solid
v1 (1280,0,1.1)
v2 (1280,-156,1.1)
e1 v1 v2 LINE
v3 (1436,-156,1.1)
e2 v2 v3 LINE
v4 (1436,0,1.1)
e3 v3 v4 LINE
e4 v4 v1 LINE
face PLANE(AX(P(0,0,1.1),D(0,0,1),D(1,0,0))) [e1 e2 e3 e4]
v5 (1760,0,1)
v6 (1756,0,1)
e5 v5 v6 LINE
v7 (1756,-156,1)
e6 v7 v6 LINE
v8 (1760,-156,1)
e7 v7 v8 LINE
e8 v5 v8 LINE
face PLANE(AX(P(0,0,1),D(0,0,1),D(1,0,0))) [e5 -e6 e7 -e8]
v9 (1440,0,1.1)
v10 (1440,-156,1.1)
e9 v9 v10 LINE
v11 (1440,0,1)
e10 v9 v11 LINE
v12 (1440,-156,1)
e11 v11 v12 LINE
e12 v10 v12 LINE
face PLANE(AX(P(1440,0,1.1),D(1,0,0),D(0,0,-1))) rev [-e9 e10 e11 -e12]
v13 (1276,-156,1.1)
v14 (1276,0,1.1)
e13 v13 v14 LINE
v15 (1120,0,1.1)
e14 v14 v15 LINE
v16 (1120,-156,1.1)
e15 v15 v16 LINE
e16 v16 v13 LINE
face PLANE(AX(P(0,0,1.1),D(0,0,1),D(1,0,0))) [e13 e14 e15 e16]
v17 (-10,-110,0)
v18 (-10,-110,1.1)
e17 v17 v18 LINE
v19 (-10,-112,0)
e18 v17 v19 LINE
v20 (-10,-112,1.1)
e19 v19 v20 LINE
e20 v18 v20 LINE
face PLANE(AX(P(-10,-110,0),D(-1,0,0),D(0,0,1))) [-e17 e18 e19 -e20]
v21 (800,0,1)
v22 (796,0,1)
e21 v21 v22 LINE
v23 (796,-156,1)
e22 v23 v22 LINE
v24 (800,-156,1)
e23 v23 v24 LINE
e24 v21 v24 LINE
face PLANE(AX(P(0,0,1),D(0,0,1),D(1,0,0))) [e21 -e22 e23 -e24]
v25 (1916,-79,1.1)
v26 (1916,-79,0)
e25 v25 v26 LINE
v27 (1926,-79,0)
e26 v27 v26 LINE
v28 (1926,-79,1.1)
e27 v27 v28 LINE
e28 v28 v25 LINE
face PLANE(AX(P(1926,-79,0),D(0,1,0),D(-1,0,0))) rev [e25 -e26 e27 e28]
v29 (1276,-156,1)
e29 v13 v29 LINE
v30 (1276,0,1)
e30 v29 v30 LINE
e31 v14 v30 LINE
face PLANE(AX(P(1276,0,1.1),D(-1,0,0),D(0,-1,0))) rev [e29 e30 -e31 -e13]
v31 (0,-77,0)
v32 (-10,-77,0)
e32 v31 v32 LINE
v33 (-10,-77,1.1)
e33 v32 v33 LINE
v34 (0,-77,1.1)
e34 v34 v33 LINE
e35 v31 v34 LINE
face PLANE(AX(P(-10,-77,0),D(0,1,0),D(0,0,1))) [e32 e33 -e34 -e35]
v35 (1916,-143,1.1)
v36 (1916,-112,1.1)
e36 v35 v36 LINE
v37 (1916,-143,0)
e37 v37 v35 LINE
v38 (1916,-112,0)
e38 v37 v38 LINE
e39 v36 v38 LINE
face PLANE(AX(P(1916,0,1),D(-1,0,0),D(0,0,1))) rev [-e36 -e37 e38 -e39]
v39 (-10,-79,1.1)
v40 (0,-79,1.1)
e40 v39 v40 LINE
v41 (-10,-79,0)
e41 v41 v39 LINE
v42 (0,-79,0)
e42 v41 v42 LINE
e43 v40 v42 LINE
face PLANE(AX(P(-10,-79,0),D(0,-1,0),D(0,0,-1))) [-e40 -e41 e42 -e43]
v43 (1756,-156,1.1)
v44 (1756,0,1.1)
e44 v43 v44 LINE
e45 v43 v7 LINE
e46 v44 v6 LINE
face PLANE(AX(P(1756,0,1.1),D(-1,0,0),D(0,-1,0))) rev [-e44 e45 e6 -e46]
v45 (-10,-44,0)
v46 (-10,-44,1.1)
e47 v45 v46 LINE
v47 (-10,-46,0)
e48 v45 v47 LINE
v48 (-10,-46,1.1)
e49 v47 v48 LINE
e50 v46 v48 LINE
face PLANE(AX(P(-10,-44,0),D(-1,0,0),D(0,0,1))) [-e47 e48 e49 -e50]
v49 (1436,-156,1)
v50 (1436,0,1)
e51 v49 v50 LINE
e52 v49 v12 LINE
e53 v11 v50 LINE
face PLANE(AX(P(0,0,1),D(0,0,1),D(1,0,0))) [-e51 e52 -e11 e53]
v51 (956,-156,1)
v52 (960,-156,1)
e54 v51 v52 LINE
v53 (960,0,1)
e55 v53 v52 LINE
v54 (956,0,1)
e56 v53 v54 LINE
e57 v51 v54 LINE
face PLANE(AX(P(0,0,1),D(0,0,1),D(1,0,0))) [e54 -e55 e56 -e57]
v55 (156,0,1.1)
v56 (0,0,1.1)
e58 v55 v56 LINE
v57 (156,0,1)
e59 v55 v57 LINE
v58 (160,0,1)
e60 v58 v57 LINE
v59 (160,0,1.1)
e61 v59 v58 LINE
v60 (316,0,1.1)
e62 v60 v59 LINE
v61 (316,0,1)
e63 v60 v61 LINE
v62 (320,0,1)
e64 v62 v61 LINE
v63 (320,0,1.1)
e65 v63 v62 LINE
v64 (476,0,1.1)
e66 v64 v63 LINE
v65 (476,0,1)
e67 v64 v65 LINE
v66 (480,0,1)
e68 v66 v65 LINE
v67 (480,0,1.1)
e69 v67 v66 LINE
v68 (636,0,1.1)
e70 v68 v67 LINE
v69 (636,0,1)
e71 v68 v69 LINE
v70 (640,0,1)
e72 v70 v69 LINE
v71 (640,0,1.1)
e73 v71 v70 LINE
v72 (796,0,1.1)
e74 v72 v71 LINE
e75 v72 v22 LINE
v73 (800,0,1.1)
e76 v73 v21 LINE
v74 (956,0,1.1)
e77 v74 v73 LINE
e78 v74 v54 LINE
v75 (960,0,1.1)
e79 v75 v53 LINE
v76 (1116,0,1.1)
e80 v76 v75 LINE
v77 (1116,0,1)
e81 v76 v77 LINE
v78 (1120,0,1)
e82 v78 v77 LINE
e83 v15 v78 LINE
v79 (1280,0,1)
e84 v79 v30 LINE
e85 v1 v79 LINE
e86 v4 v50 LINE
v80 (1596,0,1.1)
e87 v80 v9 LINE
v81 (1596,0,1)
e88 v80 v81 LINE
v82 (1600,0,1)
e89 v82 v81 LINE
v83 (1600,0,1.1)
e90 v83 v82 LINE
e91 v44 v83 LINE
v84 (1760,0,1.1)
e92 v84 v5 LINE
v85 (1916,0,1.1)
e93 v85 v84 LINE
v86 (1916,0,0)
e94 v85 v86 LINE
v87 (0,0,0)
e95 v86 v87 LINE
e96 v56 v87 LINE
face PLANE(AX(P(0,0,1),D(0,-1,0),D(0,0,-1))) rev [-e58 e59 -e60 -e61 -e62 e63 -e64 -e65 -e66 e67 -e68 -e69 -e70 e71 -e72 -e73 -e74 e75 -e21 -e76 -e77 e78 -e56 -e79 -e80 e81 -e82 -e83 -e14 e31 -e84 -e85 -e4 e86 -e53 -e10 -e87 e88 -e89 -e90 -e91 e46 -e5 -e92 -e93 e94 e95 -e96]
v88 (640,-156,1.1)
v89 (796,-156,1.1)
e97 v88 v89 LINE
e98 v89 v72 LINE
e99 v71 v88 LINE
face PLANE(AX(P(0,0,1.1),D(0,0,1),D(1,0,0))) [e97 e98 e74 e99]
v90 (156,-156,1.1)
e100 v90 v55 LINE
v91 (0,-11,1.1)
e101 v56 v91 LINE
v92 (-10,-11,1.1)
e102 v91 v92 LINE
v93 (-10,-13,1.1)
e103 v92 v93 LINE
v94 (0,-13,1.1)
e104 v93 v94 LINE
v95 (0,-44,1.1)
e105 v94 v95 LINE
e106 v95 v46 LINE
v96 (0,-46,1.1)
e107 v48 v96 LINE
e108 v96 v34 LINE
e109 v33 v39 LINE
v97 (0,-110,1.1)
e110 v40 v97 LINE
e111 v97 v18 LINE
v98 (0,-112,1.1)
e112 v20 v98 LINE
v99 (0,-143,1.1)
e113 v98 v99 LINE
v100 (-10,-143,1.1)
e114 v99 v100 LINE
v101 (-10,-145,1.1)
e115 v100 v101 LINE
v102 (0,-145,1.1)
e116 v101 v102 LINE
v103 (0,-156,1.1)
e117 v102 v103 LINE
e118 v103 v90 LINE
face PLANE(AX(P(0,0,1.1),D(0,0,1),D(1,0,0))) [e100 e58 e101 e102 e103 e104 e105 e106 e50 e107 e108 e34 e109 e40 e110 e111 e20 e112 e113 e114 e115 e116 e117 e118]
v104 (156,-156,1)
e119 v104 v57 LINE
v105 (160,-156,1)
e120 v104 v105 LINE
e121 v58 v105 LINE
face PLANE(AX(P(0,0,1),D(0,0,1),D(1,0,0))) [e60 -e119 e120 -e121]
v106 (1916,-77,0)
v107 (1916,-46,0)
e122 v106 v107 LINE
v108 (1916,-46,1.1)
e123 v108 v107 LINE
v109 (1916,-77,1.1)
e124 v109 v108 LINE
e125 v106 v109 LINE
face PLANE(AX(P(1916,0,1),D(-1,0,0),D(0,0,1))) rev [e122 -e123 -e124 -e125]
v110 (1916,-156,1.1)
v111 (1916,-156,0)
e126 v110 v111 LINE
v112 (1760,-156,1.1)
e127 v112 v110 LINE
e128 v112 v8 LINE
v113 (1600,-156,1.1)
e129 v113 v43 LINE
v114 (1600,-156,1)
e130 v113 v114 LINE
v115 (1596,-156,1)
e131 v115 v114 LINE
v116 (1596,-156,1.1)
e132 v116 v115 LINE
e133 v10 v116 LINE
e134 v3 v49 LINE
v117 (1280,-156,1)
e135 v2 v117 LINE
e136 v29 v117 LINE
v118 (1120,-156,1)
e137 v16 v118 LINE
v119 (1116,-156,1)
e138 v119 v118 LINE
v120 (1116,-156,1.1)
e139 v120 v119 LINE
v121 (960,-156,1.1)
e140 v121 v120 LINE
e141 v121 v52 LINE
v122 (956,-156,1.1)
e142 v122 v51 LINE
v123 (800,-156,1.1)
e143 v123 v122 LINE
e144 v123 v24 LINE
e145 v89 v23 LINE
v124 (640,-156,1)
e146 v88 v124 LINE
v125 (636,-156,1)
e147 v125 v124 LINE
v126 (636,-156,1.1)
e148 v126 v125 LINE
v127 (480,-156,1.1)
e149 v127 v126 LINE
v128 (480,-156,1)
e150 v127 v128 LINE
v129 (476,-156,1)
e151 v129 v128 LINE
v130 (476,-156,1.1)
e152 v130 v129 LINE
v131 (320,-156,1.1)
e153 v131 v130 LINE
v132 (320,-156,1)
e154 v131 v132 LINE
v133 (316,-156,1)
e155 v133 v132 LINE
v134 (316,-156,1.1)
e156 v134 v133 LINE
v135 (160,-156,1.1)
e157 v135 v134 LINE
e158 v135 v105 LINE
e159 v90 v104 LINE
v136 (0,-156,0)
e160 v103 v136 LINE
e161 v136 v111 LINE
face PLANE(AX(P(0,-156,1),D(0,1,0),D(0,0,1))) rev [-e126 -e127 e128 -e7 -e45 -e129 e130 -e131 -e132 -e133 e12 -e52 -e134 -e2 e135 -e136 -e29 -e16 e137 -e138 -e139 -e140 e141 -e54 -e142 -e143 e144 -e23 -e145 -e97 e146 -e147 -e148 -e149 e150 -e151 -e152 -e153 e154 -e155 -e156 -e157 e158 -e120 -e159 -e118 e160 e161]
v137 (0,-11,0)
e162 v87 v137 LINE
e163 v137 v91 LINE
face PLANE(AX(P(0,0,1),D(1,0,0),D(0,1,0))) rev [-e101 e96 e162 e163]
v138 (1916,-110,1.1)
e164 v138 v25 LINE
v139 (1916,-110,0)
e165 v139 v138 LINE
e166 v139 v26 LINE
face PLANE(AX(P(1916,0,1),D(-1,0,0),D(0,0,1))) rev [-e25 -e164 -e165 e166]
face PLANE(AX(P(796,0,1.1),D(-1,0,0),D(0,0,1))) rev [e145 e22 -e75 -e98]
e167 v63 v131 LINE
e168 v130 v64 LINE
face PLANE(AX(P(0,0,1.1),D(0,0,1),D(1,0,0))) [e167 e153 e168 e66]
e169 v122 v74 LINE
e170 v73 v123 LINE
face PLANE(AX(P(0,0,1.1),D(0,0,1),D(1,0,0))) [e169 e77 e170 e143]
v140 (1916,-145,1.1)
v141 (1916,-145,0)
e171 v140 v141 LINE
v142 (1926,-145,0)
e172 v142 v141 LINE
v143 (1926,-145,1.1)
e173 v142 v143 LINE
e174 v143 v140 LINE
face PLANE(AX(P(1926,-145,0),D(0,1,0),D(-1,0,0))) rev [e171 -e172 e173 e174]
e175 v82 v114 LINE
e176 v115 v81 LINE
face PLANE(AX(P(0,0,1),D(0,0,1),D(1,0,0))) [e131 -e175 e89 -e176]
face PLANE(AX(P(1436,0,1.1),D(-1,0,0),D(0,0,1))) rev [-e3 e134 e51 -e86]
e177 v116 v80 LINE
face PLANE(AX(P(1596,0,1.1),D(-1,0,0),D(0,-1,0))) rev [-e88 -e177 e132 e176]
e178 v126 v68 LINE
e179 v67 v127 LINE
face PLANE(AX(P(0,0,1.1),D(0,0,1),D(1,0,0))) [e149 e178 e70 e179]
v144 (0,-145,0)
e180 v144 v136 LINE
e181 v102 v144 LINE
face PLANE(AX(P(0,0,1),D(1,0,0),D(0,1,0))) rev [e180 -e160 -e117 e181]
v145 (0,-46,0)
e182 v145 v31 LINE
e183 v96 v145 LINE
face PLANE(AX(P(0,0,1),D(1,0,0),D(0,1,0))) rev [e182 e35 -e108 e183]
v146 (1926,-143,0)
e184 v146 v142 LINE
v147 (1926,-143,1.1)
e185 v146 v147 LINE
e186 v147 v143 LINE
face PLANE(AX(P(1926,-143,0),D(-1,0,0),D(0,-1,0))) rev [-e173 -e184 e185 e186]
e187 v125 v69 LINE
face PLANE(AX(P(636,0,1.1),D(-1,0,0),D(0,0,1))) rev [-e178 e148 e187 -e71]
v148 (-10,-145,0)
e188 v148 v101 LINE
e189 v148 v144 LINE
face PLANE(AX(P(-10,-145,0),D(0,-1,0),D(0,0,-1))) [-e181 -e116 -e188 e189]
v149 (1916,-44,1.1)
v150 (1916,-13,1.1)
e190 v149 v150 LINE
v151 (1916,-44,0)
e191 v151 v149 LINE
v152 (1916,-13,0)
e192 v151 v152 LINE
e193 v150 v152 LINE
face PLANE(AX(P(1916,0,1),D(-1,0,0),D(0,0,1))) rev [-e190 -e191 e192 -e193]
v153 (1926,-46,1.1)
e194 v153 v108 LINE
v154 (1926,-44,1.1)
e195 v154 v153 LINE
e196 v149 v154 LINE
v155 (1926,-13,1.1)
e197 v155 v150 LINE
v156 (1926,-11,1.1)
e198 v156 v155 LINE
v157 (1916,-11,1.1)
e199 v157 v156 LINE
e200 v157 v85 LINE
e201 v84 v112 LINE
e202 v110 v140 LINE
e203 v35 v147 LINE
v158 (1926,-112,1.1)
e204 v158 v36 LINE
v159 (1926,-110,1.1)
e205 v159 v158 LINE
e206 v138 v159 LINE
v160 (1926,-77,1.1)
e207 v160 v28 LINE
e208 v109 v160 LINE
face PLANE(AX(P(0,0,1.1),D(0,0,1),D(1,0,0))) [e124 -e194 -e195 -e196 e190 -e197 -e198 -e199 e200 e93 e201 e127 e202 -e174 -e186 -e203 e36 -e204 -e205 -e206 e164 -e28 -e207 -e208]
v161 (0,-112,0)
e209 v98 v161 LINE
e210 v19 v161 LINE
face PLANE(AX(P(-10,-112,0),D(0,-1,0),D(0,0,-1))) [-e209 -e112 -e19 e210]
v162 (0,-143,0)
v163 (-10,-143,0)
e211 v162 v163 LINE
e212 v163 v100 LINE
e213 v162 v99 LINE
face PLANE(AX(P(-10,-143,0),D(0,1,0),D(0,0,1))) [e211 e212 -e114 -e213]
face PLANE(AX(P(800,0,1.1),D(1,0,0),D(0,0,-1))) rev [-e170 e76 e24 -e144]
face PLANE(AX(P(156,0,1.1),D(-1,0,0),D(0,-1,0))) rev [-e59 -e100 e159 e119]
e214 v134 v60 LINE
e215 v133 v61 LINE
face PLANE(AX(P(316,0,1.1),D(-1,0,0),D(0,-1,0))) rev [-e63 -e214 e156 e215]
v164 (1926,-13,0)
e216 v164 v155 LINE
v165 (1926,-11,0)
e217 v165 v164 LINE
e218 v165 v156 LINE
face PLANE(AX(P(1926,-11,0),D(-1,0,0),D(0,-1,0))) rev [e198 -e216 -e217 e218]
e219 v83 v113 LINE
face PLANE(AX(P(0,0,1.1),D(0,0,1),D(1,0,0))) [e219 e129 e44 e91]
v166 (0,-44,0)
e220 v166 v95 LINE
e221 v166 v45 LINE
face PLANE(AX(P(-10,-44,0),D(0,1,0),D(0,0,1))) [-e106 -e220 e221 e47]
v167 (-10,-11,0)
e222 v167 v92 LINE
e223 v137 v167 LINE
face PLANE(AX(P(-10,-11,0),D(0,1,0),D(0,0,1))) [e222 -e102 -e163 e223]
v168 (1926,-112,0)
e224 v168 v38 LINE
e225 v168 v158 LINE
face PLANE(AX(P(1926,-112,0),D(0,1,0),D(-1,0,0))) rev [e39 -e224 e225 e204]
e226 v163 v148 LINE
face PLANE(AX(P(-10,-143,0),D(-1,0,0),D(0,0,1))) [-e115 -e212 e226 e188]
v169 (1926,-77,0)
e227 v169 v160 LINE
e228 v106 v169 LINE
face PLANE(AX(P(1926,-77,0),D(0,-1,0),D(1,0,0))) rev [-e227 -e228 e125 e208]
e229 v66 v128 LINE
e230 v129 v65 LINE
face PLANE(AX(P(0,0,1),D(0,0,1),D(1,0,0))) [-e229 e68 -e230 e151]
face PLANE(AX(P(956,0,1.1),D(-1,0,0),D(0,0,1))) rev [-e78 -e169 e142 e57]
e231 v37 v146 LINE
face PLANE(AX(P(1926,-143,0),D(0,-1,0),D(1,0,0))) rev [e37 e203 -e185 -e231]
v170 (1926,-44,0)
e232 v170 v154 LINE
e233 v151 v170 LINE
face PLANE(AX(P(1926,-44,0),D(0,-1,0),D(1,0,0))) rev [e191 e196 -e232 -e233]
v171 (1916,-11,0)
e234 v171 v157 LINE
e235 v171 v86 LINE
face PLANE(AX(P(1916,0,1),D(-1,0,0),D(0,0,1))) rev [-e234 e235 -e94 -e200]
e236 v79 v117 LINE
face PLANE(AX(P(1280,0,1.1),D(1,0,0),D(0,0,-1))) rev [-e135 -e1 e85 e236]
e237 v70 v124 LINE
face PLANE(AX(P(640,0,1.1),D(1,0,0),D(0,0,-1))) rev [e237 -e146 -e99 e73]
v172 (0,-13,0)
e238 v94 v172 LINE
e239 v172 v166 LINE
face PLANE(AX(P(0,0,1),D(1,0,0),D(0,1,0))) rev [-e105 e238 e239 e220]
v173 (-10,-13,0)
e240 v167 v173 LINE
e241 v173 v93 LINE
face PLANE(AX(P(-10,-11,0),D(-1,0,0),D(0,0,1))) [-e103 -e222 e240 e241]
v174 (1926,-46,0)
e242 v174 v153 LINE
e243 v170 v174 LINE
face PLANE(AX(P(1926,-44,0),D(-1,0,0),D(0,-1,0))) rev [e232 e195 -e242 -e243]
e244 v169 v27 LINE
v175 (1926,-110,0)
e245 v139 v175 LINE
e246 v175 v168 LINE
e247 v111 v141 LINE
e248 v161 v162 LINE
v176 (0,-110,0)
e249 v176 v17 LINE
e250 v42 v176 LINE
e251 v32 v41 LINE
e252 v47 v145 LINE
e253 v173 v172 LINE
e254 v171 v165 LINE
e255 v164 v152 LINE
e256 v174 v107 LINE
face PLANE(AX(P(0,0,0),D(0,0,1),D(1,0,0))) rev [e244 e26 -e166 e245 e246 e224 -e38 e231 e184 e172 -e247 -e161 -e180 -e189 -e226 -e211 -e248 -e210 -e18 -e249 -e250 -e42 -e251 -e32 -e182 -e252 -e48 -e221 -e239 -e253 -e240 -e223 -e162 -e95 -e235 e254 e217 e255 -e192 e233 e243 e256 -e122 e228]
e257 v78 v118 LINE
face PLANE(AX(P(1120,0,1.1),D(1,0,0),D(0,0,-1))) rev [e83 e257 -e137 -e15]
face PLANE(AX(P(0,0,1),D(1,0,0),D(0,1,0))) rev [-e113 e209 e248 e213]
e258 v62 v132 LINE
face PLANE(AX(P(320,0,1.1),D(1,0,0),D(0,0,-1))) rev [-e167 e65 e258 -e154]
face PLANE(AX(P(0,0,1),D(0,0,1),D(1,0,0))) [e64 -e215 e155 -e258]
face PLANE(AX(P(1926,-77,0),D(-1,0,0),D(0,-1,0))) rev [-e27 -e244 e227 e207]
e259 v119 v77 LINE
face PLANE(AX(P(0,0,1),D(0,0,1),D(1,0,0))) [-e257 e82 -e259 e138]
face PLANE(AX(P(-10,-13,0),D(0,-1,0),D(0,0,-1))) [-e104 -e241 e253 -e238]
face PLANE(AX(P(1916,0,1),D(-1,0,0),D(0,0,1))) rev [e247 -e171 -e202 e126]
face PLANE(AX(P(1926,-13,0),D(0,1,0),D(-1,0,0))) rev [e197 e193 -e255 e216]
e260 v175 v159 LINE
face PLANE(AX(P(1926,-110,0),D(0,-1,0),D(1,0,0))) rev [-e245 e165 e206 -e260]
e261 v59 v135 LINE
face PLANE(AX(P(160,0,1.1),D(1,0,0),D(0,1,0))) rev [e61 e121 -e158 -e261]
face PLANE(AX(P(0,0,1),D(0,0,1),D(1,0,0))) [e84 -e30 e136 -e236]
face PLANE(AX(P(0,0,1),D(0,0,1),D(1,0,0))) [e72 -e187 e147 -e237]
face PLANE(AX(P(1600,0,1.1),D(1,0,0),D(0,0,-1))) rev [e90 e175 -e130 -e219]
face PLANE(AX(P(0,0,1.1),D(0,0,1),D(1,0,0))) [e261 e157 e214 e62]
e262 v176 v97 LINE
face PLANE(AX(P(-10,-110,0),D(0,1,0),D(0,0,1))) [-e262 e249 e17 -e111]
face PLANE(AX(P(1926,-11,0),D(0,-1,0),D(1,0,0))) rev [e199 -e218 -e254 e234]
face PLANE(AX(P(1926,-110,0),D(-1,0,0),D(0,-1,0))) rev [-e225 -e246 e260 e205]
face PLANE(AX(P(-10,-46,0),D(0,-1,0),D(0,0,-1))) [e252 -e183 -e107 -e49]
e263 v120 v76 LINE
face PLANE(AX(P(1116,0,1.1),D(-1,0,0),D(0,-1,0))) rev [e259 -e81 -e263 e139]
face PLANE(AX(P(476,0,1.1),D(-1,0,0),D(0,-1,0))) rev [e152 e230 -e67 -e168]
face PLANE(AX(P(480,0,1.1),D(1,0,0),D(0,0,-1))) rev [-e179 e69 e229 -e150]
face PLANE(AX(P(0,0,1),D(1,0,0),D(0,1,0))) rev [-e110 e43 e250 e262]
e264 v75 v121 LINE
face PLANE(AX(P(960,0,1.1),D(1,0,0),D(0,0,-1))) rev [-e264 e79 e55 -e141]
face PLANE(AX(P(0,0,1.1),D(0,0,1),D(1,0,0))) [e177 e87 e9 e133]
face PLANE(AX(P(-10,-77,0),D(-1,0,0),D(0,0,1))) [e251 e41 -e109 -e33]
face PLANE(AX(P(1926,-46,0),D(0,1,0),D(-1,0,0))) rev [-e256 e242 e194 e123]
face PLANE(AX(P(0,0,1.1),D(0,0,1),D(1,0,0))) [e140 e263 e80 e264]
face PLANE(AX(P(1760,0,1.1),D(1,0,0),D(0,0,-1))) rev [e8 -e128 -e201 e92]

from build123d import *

# Parameters (mm, degrees)
SKETCH_1_W      = 1916
SKETCH_1_H      = 156
EXTRUDE_1_DEPTH = 1
SKETCH_2_W      = 156
SKETCH_2_H      = 156
EXTRUDE_2_DEPTH = 0.1
SKETCH_3_W      = 20
SKETCH_3_H      = 2
EXTRUDE_3_DEPTH = 1.1


with BuildPart() as part:
    # 草图1 → 凸台-拉伸1 (new body)
    with BuildSketch(Plane.XY):
        with Locations((958, -78)):
            Rectangle(SKETCH_1_W, SKETCH_1_H)
    extrude(amount=EXTRUDE_1_DEPTH)

    # 草图2 → 凸台-拉伸2 (add)
    with BuildSketch(Plane.XY.offset(1)):
        with Locations((78, -78)):
            Rectangle(SKETCH_2_W, SKETCH_2_H)
        with Locations((238, -78)):
            Rectangle(SKETCH_2_W, SKETCH_2_H)
        with Locations((398, -78)):
            Rectangle(SKETCH_2_W, SKETCH_2_H)
        with Locations((558, -78)):
            Rectangle(SKETCH_2_W, SKETCH_2_H)
        with Locations((718, -78)):
            Rectangle(SKETCH_2_W, SKETCH_2_H)
        with Locations((878, -78)):
            Rectangle(SKETCH_2_W, SKETCH_2_H)
        with Locations((1038, -78)):
            Rectangle(SKETCH_2_W, SKETCH_2_H)
        with Locations((1198, -78)):
            Rectangle(SKETCH_2_W, SKETCH_2_H)
        with Locations((1358, -78)):
            Rectangle(SKETCH_2_W, SKETCH_2_H)
        with Locations((1518, -78)):
            Rectangle(SKETCH_2_W, SKETCH_2_H)
        with Locations((1678, -78)):
            Rectangle(SKETCH_2_W, SKETCH_2_H)
        with Locations((1838, -78)):
            Rectangle(SKETCH_2_W, SKETCH_2_H)
    extrude(amount=EXTRUDE_2_DEPTH)

    # 草图3 → 凸台-拉伸3 (add)
    with BuildSketch(Plane.XY.offset(1.1)):
        with Locations((0, -12)):
            Rectangle(SKETCH_3_W, SKETCH_3_H)
        with Locations((0, -45)):
            Rectangle(SKETCH_3_W, SKETCH_3_H)
        with Locations((0, -78)):
            Rectangle(SKETCH_3_W, SKETCH_3_H)
        with Locations((0, -111)):
            Rectangle(SKETCH_3_W, SKETCH_3_H)
        with Locations((0, -144)):
            Rectangle(SKETCH_3_W, SKETCH_3_H)
    extrude_3 = extrude(amount=-EXTRUDE_3_DEPTH)

    # 镜向1: 凸台-拉伸3 across plane
    add(extrude_3.mirror(Plane.ZY.offset(-958)))


solid = part.part
